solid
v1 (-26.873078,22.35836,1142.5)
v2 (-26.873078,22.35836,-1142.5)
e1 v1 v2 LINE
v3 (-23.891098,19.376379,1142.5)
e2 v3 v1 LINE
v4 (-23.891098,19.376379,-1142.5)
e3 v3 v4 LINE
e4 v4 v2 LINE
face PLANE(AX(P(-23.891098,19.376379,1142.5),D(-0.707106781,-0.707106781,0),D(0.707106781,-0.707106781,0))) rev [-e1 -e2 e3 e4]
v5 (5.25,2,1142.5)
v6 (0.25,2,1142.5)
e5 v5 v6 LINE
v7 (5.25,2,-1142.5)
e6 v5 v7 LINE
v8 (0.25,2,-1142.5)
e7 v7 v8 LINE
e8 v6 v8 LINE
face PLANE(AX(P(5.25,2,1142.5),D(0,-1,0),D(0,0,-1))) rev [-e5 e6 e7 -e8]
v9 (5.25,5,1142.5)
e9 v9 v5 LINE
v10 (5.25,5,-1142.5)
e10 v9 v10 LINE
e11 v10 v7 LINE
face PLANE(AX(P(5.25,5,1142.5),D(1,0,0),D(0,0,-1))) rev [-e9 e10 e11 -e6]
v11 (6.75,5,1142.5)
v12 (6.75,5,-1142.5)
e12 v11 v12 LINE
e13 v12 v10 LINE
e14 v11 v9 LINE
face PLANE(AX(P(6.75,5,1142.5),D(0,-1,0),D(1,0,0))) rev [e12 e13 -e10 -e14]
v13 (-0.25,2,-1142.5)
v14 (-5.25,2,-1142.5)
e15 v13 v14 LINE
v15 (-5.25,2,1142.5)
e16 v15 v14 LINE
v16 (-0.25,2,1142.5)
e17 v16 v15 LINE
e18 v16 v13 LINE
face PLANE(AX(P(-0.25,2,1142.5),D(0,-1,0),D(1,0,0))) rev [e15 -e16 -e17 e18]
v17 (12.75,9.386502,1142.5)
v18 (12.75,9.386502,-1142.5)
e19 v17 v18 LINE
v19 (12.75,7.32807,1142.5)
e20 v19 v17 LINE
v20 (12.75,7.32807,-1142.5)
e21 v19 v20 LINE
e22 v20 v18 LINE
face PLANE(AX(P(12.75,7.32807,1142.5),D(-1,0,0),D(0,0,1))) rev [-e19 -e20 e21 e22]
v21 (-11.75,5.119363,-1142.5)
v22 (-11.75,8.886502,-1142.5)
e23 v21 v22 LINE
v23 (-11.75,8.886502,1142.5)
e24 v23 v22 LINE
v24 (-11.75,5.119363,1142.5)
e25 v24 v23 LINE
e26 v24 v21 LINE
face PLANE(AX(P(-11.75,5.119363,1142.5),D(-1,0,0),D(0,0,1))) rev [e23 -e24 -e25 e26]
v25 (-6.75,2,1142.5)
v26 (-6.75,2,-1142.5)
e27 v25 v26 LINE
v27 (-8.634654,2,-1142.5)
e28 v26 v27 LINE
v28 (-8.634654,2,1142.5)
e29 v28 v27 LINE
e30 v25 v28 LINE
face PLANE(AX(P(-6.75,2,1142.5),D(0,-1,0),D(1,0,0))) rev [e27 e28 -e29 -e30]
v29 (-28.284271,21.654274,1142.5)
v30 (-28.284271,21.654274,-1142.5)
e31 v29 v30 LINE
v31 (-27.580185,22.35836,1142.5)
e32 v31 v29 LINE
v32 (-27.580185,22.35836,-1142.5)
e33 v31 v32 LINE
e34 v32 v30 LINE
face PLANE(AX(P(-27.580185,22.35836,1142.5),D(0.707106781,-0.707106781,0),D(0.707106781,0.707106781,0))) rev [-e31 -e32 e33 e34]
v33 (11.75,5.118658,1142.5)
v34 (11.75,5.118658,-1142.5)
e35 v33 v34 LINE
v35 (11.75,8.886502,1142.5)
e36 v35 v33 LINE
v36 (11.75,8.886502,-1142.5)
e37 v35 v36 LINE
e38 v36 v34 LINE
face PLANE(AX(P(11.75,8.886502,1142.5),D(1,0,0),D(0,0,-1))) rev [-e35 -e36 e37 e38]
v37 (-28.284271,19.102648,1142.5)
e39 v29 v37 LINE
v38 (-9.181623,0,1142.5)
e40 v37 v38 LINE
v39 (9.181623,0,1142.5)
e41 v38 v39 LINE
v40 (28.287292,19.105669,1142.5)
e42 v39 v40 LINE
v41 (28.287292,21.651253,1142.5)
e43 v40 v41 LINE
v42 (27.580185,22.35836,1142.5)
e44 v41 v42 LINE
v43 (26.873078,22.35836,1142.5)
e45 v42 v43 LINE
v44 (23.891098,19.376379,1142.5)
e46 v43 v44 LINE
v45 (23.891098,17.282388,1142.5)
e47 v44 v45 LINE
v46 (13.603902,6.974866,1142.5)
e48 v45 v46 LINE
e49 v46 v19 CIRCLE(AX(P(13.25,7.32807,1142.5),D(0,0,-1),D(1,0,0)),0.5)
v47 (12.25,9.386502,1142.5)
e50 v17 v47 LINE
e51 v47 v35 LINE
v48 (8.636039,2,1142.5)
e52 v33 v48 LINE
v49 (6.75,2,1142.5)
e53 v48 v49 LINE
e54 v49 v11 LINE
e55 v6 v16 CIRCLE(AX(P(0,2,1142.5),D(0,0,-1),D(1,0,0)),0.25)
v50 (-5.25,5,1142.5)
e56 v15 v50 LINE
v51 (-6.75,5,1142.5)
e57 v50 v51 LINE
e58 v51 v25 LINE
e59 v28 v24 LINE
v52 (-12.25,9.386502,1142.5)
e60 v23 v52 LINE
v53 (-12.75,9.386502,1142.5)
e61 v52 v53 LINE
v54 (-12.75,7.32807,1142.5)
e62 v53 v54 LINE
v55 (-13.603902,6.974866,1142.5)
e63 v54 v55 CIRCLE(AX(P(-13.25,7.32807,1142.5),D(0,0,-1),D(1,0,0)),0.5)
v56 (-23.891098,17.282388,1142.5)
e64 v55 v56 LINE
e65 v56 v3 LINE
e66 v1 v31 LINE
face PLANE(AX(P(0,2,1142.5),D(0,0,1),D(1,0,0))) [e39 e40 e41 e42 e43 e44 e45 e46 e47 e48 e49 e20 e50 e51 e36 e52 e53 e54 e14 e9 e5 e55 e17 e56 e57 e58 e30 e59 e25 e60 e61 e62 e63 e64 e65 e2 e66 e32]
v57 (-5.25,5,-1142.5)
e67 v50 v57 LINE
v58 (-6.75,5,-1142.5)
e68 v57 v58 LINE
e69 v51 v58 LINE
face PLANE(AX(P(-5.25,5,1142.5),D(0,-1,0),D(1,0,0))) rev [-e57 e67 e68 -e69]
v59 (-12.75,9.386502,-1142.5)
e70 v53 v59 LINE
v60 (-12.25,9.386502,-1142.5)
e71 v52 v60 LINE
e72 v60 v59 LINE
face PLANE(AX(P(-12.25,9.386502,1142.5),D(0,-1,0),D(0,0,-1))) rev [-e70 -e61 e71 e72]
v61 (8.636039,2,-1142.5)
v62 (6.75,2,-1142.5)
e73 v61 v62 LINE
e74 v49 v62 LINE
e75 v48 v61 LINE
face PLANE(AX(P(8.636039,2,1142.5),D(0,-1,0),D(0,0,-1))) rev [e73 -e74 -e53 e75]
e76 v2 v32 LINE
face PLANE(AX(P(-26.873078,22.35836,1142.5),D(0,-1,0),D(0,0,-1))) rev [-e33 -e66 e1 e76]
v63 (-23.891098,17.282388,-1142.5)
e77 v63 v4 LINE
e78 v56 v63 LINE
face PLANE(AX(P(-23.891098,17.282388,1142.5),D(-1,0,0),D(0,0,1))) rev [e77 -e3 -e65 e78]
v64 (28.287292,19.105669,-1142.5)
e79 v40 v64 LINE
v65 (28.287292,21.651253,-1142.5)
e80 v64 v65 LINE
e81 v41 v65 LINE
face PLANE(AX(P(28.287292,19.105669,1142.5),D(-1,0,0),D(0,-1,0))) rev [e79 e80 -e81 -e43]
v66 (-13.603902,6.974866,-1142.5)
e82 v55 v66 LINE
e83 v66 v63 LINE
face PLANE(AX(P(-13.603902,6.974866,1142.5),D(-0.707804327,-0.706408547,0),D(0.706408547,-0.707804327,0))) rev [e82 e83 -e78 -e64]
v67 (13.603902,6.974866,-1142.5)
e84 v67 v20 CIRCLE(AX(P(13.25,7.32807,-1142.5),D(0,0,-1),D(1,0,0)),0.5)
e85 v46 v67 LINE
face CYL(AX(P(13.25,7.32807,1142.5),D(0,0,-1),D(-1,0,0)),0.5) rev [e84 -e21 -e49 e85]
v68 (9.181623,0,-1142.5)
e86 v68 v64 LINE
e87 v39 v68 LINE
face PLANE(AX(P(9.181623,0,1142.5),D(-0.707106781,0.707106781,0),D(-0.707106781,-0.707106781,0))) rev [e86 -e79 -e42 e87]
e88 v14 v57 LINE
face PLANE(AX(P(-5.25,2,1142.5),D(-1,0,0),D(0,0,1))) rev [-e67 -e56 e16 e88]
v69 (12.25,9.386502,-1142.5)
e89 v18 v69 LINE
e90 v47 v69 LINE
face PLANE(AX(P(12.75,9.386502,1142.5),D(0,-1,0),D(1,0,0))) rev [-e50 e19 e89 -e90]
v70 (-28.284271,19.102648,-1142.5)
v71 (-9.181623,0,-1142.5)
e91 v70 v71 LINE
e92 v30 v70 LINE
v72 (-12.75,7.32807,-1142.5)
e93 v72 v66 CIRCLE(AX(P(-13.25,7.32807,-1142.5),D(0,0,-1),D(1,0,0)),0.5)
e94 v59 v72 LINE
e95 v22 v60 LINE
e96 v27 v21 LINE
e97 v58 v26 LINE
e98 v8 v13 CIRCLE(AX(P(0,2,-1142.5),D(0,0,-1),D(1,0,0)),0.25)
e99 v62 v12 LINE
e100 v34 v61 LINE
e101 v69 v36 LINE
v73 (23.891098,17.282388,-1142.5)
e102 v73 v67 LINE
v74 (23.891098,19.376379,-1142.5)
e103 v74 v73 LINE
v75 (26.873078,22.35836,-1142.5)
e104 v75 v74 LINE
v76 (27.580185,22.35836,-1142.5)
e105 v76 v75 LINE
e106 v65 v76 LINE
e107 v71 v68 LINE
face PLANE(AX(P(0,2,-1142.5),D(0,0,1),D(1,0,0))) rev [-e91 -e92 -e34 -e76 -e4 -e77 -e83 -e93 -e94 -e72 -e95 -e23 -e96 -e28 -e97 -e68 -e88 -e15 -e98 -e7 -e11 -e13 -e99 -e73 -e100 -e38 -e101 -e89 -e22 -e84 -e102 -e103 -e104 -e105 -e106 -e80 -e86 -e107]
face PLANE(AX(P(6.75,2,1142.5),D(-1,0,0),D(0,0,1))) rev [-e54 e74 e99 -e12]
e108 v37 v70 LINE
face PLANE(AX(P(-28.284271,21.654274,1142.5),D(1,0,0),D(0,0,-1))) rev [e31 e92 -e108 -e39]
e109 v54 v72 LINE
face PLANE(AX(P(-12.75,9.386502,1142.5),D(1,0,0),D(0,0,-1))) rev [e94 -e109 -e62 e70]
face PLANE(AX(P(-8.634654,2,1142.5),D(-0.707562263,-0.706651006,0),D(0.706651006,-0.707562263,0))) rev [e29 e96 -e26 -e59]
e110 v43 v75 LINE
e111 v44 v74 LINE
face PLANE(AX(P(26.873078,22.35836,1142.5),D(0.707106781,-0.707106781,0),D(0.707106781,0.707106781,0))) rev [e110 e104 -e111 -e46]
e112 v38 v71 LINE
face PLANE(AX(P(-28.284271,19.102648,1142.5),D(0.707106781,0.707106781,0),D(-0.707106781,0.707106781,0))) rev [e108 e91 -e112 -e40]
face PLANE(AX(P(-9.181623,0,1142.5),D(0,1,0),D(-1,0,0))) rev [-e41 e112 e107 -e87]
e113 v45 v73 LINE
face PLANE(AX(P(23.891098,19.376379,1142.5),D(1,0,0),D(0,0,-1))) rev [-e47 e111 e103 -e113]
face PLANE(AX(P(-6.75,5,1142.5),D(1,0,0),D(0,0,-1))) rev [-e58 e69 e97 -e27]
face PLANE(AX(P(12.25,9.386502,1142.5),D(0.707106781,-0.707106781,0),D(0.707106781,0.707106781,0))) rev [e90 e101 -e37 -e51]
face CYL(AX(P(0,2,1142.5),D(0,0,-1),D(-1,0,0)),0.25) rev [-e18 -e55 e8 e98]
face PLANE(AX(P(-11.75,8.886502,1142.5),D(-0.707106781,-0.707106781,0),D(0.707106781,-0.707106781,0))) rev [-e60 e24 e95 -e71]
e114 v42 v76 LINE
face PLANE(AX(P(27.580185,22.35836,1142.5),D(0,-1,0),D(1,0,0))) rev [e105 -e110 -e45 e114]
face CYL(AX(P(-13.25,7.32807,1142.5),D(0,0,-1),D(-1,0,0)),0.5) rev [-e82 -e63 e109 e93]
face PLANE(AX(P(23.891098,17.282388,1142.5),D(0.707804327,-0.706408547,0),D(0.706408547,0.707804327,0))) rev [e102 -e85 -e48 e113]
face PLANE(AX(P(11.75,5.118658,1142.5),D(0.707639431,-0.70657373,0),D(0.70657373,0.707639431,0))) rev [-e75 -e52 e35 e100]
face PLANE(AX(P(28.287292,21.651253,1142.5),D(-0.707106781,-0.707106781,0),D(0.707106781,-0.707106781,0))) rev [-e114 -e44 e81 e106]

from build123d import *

# Parameters (mm, degrees)
EXTRUDE_1_DEPTH = 1142.5


with BuildPart() as part:
    # 草图2 → 凸台-拉伸1 (new, symmetric)
    with BuildSketch(Plane.XY):
        with BuildLine():
            Line((6.75, 5), (5.25, 5))
            Line((5.25, 5), (5.25, 2))
            Line((5.25, 2), (0.25, 2))
            ThreePointArc((0.25, 2), (0, 1.75), (-0.25, 2))
            Line((-0.25, 2), (-5.25, 2))
            Line((-5.25, 2), (-5.25, 5))
            Line((-5.25, 5), (-6.75, 5))
            Line((-6.75, 5), (-6.75, 2))
            Line((-6.75, 2), (-8.634653896, 2))
            Line((-8.634653896, 2), (-11.75, 5.119363474))
            Line((-11.75, 5.119363474), (-11.75, 8.88650173))
            Line((-11.75, 8.88650173), (-12.25, 9.38650173))
            Line((-12.25, 9.38650173), (-12.75, 9.38650173))
            Line((-12.75, 9.38650173), (-12.75, 7.328070483))
            ThreePointArc((-12.75, 7.328070483), (-13.058886266, 6.866036349), (-13.603902163, 6.97486621))
            Line((-13.603902163, 6.97486621), (-23.891097866, 17.282388203))
            Line((-23.891097866, 17.282388203), (-23.891097866, 19.37637924))
            Line((-23.891097866, 19.37637924), (-26.873078382, 22.358359756))
            Line((-26.873078382, 22.358359756), (-27.580185163, 22.358359756))
            Line((-27.580185163, 22.358359756), (-28.284271248, 21.654273671))
            Line((-28.284271248, 21.654273671), (-28.284271248, 19.102647866))
            Line((-28.284271248, 19.102647866), (-9.181623382, 0))
            Line((-9.181623382, 0), (9.181623382, 0))
            Line((9.181623382, 0), (28.287291944, 19.105668562))
            Line((28.287291944, 19.105668562), (28.287291944, 21.651252975))
            Line((28.287291944, 21.651252975), (27.580185163, 22.358359756))
            Line((27.580185163, 22.358359756), (26.873078382, 22.358359756))
            Line((26.873078382, 22.358359756), (23.891097866, 19.376379241))
            Line((23.891097866, 19.376379241), (23.891097866, 17.282388203))
            Line((23.891097866, 17.282388203), (13.603902163, 6.97486621))
            ThreePointArc((13.603902163, 6.97486621), (13.058886266, 6.866036349), (12.75, 7.328070483))
            Line((12.75, 7.328070483), (12.75, 9.38650173))
            Line((12.75, 9.38650173), (12.25, 9.38650173))
            Line((12.25, 9.38650173), (11.75, 8.88650173))
            Line((11.75, 8.88650173), (11.75, 5.118657708))
            Line((11.75, 5.118657708), (8.636038969, 2))
            Line((8.636038969, 2), (6.75, 2))
            Line((6.75, 2), (6.75, 5))
        make_face()
    extrude(amount=EXTRUDE_1_DEPTH, both=True)


solid = part.part
